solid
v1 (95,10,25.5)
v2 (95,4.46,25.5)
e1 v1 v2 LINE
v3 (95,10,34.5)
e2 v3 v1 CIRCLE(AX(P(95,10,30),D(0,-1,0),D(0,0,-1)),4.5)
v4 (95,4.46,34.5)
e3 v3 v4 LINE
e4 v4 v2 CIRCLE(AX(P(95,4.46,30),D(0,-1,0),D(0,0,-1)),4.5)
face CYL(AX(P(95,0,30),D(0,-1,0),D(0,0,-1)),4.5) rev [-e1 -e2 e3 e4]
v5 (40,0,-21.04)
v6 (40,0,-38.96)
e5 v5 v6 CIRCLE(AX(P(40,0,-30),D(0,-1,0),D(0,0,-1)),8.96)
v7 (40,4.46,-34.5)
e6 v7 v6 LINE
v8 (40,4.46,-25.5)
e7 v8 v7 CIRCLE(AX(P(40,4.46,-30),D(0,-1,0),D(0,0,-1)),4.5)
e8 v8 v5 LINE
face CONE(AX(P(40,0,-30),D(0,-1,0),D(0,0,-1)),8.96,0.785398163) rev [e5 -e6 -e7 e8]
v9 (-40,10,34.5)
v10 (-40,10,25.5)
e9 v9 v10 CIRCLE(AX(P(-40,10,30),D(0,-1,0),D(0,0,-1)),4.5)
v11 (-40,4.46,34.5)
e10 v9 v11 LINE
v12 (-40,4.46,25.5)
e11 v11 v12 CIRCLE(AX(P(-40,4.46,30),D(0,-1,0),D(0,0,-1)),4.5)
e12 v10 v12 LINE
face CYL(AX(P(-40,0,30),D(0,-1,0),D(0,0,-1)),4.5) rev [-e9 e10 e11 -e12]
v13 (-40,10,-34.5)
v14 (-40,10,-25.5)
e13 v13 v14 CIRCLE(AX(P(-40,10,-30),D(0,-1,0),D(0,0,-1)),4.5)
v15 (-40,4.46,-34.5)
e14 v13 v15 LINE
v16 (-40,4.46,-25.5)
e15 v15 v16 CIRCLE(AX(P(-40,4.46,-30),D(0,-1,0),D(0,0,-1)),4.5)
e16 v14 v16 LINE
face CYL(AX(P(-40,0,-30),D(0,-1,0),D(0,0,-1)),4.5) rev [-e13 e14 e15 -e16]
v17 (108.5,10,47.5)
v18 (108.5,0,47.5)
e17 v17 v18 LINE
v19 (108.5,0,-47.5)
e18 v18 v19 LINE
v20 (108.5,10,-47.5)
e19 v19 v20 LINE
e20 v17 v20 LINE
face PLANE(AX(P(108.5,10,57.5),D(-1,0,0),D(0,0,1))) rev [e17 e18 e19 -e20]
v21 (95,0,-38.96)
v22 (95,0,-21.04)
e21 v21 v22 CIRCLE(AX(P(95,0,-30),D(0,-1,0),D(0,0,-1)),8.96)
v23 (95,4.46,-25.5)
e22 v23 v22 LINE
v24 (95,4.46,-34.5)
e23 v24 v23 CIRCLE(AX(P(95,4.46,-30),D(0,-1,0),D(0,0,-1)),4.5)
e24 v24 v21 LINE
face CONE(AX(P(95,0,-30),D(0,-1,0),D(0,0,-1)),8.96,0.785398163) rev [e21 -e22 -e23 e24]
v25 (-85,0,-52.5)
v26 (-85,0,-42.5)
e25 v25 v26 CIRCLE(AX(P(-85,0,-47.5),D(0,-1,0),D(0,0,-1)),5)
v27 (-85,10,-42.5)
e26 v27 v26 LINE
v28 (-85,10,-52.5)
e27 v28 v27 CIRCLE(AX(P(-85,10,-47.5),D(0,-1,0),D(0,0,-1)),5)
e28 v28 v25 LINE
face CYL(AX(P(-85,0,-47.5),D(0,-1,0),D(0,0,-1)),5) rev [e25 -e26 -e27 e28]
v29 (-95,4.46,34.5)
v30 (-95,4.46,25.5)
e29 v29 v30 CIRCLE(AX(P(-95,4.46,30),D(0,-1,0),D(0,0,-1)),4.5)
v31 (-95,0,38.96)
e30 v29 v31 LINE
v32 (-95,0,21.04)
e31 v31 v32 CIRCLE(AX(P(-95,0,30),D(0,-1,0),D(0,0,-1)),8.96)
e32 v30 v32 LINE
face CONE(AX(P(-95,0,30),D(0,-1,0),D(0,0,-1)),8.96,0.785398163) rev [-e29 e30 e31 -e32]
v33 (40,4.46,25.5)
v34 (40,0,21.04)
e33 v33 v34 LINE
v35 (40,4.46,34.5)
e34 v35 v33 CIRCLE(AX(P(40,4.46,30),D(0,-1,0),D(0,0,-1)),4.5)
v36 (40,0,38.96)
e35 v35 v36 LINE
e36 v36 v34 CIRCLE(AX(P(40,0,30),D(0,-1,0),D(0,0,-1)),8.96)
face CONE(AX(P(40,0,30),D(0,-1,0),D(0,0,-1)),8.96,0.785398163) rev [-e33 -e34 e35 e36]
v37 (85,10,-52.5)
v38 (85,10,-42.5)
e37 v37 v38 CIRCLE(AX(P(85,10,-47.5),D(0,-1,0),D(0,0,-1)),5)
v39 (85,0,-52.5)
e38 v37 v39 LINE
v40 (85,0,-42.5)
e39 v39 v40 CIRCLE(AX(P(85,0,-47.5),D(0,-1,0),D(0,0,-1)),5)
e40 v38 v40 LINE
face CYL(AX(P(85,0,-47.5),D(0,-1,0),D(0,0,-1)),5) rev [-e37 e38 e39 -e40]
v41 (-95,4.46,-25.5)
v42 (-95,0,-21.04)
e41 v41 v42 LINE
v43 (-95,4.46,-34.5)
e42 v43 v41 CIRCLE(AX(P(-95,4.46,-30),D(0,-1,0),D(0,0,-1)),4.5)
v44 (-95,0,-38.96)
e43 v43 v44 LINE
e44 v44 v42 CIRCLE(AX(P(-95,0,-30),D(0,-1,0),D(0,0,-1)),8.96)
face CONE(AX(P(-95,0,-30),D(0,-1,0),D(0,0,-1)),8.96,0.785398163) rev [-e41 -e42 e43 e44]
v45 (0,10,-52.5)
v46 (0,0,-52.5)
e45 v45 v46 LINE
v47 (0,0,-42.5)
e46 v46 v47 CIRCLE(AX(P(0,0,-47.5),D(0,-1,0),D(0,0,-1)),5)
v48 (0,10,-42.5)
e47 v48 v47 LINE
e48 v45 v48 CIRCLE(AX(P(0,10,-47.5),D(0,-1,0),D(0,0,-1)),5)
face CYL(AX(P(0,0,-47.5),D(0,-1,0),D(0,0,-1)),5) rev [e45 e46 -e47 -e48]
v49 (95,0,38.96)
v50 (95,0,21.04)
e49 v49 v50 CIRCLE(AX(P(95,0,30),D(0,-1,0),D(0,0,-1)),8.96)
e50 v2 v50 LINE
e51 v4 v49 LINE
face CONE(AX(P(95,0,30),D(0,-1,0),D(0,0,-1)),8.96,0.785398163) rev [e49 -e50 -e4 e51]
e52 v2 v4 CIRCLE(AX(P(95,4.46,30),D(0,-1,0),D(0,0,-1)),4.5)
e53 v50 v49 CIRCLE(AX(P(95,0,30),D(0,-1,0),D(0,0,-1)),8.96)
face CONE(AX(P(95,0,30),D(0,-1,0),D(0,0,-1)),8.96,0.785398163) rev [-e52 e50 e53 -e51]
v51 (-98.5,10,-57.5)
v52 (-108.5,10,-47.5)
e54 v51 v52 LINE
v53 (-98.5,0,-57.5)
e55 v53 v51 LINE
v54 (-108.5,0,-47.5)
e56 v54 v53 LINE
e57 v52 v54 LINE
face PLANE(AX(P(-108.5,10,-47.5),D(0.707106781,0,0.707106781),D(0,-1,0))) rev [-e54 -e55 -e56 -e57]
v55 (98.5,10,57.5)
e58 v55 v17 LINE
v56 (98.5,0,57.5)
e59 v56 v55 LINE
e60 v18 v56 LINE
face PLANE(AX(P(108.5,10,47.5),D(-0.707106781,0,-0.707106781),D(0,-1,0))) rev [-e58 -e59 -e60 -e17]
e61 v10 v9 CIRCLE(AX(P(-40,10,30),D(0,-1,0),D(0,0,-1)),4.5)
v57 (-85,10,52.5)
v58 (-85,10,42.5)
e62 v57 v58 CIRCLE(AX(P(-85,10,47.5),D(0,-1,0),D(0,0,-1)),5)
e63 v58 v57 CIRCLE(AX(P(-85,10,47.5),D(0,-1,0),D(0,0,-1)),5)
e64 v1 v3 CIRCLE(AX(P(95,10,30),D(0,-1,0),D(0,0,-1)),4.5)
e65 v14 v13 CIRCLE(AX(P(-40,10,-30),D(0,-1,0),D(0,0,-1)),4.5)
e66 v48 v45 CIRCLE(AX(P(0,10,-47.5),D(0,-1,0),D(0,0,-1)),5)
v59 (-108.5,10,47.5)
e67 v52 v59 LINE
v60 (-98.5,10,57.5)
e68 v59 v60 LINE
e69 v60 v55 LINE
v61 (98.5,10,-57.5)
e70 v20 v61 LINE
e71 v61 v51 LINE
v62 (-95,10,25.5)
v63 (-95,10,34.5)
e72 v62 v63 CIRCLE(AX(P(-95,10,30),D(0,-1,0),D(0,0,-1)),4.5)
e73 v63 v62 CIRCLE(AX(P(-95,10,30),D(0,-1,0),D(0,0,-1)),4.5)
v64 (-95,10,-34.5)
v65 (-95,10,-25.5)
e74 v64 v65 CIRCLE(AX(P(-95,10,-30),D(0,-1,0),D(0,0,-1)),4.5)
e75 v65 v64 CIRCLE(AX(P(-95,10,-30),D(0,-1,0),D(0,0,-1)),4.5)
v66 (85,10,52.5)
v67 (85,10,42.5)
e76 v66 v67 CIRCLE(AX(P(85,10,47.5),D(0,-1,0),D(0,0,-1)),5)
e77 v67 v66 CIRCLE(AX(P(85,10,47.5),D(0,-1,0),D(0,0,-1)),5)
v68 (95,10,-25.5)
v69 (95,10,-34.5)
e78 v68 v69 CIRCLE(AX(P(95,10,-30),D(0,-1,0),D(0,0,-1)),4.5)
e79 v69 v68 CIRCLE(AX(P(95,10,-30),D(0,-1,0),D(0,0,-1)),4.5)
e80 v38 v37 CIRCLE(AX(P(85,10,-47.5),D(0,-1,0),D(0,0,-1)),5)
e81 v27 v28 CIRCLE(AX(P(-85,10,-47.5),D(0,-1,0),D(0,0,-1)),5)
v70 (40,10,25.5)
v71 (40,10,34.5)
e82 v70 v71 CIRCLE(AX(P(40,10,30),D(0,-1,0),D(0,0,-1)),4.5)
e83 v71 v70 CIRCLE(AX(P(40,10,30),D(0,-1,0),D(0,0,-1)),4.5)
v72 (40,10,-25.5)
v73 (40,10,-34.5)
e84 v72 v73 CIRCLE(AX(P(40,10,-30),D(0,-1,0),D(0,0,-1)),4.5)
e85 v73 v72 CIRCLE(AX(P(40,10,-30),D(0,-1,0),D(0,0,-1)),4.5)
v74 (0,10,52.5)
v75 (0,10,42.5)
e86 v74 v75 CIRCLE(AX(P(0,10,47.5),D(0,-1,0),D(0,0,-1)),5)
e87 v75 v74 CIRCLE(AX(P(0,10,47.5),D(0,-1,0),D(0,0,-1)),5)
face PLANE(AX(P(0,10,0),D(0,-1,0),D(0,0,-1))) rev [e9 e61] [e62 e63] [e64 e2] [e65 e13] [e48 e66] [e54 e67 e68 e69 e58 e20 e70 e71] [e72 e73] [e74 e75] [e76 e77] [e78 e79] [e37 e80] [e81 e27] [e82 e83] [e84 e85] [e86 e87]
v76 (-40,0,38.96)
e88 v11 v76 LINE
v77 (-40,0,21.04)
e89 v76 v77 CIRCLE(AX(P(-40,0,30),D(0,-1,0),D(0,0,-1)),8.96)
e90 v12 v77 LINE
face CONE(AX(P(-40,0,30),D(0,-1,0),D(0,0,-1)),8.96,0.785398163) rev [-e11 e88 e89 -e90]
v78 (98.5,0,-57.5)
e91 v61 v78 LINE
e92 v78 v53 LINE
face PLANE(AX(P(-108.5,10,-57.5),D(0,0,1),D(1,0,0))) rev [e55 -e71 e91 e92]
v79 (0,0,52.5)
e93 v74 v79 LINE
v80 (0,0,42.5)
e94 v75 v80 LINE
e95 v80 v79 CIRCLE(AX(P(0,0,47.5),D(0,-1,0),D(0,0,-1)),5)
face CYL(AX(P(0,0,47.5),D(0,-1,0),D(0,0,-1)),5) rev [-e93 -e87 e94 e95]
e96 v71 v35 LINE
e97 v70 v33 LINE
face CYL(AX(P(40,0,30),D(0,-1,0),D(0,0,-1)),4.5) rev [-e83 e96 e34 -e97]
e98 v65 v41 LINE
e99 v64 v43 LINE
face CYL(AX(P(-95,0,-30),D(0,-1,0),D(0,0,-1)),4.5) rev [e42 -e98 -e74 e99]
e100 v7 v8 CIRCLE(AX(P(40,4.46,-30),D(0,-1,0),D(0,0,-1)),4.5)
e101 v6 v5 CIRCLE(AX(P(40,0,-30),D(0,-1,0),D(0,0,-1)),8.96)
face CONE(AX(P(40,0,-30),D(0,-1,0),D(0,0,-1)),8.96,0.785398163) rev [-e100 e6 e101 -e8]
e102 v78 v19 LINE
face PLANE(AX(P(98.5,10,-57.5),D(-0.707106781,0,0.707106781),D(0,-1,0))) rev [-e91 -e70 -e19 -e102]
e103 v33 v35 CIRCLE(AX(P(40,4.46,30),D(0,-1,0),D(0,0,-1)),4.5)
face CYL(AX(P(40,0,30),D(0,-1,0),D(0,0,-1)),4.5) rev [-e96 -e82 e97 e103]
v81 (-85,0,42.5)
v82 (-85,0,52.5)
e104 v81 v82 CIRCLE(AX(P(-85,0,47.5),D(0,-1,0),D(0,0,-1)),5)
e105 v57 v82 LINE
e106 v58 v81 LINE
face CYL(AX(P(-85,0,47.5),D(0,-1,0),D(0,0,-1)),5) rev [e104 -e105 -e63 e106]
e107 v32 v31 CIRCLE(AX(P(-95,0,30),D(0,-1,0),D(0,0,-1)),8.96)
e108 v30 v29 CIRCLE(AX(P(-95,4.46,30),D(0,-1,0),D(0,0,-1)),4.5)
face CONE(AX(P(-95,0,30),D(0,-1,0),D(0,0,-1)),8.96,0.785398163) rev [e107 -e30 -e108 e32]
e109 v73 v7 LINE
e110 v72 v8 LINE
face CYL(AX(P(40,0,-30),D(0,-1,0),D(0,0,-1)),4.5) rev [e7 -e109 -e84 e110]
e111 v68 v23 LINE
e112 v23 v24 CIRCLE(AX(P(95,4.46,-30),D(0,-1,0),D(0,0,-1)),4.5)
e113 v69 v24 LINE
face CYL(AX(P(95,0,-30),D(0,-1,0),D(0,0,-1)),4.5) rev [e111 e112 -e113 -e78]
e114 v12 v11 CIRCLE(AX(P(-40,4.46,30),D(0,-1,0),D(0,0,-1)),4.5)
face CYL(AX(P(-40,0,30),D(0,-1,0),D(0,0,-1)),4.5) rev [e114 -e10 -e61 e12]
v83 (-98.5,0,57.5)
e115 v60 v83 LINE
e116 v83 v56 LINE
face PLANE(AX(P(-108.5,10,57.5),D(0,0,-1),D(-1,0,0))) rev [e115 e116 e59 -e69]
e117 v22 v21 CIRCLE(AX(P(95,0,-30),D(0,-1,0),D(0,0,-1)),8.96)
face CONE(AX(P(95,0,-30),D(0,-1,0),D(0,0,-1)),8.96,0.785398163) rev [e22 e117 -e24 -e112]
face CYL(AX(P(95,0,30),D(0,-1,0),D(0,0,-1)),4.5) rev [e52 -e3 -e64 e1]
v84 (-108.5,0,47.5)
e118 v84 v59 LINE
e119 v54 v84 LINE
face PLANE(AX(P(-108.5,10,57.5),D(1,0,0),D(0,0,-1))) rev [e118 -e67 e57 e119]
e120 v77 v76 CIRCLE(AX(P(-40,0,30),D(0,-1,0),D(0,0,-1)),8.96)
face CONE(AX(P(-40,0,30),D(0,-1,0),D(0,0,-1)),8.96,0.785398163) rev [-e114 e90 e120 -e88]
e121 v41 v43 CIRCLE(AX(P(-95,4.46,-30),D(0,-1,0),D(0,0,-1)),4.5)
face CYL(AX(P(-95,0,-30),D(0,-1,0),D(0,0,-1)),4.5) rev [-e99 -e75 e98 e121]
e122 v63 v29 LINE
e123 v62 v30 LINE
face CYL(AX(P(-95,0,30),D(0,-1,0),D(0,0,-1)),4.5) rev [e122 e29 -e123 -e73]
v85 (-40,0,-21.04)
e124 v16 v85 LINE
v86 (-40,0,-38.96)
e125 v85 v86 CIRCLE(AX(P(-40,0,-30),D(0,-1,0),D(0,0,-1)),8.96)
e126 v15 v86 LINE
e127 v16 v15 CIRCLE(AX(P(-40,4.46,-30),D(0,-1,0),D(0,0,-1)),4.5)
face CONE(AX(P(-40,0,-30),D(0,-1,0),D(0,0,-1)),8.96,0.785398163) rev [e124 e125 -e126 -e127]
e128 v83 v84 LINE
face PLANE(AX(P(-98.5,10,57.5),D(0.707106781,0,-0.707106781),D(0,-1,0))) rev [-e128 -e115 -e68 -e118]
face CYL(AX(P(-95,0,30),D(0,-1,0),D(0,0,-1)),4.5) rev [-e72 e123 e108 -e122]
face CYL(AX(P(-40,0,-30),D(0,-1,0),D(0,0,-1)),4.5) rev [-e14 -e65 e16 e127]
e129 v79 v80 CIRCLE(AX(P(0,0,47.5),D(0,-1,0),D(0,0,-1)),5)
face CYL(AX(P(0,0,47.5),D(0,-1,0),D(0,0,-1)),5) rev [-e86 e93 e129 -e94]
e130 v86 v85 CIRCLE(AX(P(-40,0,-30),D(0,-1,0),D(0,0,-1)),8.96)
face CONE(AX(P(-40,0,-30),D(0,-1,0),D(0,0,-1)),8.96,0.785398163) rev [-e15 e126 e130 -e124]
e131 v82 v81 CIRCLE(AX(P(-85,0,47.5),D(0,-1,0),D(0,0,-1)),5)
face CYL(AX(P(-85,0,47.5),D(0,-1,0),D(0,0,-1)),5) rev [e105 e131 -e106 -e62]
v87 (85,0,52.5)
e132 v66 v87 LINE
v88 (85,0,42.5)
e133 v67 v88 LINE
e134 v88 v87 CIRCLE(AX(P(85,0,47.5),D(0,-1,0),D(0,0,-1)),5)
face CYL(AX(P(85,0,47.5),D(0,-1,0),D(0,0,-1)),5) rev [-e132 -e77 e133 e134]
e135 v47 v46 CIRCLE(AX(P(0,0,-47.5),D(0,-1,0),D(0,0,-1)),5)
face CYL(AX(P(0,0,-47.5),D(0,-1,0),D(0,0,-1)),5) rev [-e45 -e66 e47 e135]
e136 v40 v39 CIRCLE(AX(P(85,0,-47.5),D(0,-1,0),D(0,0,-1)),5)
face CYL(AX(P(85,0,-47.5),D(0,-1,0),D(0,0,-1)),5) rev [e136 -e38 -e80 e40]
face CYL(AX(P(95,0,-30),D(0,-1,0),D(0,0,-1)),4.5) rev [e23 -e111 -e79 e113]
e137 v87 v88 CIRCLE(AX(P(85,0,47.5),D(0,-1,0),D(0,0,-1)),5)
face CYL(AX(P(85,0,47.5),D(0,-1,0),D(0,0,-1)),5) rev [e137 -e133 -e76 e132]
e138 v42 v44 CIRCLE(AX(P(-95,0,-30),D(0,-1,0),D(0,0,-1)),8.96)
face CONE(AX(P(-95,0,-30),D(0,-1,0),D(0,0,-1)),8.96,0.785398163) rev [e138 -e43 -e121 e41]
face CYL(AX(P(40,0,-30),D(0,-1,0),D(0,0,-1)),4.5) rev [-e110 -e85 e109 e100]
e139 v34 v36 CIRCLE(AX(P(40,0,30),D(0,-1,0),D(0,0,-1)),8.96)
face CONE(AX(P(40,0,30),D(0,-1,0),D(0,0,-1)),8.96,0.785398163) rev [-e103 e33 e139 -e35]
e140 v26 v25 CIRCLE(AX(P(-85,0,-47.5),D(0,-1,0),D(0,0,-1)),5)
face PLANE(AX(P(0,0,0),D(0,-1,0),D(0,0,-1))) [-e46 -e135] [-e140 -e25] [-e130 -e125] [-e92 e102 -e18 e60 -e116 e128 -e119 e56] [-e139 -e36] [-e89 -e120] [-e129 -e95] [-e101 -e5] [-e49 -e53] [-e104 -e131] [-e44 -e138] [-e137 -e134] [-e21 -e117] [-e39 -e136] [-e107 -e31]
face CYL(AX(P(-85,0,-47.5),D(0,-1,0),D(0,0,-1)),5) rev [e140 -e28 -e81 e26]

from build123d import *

# Parameters (mm, degrees)
SKETCH_1_W                   = 217
SKETCH_1_H                   = 115
EXTRUDE_1_DEPTH              = 10
HOLE_WIZARD_M8_1_D           = 9
HOLE_WIZARD_M8_1_CSINK_D     = 17.92
HOLE_WIZARD_M8_1_CSINK_ANGLE = 90
HOLE_WIZARD_M8_2_D           = 10
CHAMFER_1_SIZE               = 10


with BuildPart() as part:
    # 草图1 → 凸台-拉伸1 (new body)
    with BuildSketch(Plane(origin=(0, 0, 0), x_dir=(1, 0, 0), z_dir=(0, 1, 0))):
        Rectangle(SKETCH_1_W, SKETCH_1_H)
    extrude(amount=EXTRUDE_1_DEPTH)

    # M8 六角凹锥坑螺钉的锥形沉头孔1 (through all)
    with Locations(Plane(origin=(0, 0, 0), x_dir=(-1, 0, 0), z_dir=(0, -1, 0))):
        with Locations((-95, -30), (-40, -30), (40, -30), (95, -30), (95, 30), (40, 30), (-40, 30), (-95, 30)):
            CounterSinkHole(HOLE_WIZARD_M8_1_D / 2, HOLE_WIZARD_M8_1_CSINK_D / 2, counter_sink_angle=HOLE_WIZARD_M8_1_CSINK_ANGLE)

    # M8 间隙孔2 (through all)
    with Locations(Plane(origin=(0, 0, 0), x_dir=(-1, 0, 0), z_dir=(0, -1, 0))):
        with Locations((-85, 47.5), (0, 47.5), (85, 47.5), (85, -47.5), (0, -47.5), (-85, -47.5)):
            Hole(HOLE_WIZARD_M8_2_D / 2)

    # 倒角1
    chamfer_1_edges = [part.edges().sort_by_distance(p)[0] for p in [
        (108.5, 5, 57.5),
        (-108.5, 5, 57.5),
        (-108.5, 5, -57.5),
        (108.5, 5, -57.5),
    ]]
    chamfer(chamfer_1_edges, length=CHAMFER_1_SIZE)


solid = part.part
